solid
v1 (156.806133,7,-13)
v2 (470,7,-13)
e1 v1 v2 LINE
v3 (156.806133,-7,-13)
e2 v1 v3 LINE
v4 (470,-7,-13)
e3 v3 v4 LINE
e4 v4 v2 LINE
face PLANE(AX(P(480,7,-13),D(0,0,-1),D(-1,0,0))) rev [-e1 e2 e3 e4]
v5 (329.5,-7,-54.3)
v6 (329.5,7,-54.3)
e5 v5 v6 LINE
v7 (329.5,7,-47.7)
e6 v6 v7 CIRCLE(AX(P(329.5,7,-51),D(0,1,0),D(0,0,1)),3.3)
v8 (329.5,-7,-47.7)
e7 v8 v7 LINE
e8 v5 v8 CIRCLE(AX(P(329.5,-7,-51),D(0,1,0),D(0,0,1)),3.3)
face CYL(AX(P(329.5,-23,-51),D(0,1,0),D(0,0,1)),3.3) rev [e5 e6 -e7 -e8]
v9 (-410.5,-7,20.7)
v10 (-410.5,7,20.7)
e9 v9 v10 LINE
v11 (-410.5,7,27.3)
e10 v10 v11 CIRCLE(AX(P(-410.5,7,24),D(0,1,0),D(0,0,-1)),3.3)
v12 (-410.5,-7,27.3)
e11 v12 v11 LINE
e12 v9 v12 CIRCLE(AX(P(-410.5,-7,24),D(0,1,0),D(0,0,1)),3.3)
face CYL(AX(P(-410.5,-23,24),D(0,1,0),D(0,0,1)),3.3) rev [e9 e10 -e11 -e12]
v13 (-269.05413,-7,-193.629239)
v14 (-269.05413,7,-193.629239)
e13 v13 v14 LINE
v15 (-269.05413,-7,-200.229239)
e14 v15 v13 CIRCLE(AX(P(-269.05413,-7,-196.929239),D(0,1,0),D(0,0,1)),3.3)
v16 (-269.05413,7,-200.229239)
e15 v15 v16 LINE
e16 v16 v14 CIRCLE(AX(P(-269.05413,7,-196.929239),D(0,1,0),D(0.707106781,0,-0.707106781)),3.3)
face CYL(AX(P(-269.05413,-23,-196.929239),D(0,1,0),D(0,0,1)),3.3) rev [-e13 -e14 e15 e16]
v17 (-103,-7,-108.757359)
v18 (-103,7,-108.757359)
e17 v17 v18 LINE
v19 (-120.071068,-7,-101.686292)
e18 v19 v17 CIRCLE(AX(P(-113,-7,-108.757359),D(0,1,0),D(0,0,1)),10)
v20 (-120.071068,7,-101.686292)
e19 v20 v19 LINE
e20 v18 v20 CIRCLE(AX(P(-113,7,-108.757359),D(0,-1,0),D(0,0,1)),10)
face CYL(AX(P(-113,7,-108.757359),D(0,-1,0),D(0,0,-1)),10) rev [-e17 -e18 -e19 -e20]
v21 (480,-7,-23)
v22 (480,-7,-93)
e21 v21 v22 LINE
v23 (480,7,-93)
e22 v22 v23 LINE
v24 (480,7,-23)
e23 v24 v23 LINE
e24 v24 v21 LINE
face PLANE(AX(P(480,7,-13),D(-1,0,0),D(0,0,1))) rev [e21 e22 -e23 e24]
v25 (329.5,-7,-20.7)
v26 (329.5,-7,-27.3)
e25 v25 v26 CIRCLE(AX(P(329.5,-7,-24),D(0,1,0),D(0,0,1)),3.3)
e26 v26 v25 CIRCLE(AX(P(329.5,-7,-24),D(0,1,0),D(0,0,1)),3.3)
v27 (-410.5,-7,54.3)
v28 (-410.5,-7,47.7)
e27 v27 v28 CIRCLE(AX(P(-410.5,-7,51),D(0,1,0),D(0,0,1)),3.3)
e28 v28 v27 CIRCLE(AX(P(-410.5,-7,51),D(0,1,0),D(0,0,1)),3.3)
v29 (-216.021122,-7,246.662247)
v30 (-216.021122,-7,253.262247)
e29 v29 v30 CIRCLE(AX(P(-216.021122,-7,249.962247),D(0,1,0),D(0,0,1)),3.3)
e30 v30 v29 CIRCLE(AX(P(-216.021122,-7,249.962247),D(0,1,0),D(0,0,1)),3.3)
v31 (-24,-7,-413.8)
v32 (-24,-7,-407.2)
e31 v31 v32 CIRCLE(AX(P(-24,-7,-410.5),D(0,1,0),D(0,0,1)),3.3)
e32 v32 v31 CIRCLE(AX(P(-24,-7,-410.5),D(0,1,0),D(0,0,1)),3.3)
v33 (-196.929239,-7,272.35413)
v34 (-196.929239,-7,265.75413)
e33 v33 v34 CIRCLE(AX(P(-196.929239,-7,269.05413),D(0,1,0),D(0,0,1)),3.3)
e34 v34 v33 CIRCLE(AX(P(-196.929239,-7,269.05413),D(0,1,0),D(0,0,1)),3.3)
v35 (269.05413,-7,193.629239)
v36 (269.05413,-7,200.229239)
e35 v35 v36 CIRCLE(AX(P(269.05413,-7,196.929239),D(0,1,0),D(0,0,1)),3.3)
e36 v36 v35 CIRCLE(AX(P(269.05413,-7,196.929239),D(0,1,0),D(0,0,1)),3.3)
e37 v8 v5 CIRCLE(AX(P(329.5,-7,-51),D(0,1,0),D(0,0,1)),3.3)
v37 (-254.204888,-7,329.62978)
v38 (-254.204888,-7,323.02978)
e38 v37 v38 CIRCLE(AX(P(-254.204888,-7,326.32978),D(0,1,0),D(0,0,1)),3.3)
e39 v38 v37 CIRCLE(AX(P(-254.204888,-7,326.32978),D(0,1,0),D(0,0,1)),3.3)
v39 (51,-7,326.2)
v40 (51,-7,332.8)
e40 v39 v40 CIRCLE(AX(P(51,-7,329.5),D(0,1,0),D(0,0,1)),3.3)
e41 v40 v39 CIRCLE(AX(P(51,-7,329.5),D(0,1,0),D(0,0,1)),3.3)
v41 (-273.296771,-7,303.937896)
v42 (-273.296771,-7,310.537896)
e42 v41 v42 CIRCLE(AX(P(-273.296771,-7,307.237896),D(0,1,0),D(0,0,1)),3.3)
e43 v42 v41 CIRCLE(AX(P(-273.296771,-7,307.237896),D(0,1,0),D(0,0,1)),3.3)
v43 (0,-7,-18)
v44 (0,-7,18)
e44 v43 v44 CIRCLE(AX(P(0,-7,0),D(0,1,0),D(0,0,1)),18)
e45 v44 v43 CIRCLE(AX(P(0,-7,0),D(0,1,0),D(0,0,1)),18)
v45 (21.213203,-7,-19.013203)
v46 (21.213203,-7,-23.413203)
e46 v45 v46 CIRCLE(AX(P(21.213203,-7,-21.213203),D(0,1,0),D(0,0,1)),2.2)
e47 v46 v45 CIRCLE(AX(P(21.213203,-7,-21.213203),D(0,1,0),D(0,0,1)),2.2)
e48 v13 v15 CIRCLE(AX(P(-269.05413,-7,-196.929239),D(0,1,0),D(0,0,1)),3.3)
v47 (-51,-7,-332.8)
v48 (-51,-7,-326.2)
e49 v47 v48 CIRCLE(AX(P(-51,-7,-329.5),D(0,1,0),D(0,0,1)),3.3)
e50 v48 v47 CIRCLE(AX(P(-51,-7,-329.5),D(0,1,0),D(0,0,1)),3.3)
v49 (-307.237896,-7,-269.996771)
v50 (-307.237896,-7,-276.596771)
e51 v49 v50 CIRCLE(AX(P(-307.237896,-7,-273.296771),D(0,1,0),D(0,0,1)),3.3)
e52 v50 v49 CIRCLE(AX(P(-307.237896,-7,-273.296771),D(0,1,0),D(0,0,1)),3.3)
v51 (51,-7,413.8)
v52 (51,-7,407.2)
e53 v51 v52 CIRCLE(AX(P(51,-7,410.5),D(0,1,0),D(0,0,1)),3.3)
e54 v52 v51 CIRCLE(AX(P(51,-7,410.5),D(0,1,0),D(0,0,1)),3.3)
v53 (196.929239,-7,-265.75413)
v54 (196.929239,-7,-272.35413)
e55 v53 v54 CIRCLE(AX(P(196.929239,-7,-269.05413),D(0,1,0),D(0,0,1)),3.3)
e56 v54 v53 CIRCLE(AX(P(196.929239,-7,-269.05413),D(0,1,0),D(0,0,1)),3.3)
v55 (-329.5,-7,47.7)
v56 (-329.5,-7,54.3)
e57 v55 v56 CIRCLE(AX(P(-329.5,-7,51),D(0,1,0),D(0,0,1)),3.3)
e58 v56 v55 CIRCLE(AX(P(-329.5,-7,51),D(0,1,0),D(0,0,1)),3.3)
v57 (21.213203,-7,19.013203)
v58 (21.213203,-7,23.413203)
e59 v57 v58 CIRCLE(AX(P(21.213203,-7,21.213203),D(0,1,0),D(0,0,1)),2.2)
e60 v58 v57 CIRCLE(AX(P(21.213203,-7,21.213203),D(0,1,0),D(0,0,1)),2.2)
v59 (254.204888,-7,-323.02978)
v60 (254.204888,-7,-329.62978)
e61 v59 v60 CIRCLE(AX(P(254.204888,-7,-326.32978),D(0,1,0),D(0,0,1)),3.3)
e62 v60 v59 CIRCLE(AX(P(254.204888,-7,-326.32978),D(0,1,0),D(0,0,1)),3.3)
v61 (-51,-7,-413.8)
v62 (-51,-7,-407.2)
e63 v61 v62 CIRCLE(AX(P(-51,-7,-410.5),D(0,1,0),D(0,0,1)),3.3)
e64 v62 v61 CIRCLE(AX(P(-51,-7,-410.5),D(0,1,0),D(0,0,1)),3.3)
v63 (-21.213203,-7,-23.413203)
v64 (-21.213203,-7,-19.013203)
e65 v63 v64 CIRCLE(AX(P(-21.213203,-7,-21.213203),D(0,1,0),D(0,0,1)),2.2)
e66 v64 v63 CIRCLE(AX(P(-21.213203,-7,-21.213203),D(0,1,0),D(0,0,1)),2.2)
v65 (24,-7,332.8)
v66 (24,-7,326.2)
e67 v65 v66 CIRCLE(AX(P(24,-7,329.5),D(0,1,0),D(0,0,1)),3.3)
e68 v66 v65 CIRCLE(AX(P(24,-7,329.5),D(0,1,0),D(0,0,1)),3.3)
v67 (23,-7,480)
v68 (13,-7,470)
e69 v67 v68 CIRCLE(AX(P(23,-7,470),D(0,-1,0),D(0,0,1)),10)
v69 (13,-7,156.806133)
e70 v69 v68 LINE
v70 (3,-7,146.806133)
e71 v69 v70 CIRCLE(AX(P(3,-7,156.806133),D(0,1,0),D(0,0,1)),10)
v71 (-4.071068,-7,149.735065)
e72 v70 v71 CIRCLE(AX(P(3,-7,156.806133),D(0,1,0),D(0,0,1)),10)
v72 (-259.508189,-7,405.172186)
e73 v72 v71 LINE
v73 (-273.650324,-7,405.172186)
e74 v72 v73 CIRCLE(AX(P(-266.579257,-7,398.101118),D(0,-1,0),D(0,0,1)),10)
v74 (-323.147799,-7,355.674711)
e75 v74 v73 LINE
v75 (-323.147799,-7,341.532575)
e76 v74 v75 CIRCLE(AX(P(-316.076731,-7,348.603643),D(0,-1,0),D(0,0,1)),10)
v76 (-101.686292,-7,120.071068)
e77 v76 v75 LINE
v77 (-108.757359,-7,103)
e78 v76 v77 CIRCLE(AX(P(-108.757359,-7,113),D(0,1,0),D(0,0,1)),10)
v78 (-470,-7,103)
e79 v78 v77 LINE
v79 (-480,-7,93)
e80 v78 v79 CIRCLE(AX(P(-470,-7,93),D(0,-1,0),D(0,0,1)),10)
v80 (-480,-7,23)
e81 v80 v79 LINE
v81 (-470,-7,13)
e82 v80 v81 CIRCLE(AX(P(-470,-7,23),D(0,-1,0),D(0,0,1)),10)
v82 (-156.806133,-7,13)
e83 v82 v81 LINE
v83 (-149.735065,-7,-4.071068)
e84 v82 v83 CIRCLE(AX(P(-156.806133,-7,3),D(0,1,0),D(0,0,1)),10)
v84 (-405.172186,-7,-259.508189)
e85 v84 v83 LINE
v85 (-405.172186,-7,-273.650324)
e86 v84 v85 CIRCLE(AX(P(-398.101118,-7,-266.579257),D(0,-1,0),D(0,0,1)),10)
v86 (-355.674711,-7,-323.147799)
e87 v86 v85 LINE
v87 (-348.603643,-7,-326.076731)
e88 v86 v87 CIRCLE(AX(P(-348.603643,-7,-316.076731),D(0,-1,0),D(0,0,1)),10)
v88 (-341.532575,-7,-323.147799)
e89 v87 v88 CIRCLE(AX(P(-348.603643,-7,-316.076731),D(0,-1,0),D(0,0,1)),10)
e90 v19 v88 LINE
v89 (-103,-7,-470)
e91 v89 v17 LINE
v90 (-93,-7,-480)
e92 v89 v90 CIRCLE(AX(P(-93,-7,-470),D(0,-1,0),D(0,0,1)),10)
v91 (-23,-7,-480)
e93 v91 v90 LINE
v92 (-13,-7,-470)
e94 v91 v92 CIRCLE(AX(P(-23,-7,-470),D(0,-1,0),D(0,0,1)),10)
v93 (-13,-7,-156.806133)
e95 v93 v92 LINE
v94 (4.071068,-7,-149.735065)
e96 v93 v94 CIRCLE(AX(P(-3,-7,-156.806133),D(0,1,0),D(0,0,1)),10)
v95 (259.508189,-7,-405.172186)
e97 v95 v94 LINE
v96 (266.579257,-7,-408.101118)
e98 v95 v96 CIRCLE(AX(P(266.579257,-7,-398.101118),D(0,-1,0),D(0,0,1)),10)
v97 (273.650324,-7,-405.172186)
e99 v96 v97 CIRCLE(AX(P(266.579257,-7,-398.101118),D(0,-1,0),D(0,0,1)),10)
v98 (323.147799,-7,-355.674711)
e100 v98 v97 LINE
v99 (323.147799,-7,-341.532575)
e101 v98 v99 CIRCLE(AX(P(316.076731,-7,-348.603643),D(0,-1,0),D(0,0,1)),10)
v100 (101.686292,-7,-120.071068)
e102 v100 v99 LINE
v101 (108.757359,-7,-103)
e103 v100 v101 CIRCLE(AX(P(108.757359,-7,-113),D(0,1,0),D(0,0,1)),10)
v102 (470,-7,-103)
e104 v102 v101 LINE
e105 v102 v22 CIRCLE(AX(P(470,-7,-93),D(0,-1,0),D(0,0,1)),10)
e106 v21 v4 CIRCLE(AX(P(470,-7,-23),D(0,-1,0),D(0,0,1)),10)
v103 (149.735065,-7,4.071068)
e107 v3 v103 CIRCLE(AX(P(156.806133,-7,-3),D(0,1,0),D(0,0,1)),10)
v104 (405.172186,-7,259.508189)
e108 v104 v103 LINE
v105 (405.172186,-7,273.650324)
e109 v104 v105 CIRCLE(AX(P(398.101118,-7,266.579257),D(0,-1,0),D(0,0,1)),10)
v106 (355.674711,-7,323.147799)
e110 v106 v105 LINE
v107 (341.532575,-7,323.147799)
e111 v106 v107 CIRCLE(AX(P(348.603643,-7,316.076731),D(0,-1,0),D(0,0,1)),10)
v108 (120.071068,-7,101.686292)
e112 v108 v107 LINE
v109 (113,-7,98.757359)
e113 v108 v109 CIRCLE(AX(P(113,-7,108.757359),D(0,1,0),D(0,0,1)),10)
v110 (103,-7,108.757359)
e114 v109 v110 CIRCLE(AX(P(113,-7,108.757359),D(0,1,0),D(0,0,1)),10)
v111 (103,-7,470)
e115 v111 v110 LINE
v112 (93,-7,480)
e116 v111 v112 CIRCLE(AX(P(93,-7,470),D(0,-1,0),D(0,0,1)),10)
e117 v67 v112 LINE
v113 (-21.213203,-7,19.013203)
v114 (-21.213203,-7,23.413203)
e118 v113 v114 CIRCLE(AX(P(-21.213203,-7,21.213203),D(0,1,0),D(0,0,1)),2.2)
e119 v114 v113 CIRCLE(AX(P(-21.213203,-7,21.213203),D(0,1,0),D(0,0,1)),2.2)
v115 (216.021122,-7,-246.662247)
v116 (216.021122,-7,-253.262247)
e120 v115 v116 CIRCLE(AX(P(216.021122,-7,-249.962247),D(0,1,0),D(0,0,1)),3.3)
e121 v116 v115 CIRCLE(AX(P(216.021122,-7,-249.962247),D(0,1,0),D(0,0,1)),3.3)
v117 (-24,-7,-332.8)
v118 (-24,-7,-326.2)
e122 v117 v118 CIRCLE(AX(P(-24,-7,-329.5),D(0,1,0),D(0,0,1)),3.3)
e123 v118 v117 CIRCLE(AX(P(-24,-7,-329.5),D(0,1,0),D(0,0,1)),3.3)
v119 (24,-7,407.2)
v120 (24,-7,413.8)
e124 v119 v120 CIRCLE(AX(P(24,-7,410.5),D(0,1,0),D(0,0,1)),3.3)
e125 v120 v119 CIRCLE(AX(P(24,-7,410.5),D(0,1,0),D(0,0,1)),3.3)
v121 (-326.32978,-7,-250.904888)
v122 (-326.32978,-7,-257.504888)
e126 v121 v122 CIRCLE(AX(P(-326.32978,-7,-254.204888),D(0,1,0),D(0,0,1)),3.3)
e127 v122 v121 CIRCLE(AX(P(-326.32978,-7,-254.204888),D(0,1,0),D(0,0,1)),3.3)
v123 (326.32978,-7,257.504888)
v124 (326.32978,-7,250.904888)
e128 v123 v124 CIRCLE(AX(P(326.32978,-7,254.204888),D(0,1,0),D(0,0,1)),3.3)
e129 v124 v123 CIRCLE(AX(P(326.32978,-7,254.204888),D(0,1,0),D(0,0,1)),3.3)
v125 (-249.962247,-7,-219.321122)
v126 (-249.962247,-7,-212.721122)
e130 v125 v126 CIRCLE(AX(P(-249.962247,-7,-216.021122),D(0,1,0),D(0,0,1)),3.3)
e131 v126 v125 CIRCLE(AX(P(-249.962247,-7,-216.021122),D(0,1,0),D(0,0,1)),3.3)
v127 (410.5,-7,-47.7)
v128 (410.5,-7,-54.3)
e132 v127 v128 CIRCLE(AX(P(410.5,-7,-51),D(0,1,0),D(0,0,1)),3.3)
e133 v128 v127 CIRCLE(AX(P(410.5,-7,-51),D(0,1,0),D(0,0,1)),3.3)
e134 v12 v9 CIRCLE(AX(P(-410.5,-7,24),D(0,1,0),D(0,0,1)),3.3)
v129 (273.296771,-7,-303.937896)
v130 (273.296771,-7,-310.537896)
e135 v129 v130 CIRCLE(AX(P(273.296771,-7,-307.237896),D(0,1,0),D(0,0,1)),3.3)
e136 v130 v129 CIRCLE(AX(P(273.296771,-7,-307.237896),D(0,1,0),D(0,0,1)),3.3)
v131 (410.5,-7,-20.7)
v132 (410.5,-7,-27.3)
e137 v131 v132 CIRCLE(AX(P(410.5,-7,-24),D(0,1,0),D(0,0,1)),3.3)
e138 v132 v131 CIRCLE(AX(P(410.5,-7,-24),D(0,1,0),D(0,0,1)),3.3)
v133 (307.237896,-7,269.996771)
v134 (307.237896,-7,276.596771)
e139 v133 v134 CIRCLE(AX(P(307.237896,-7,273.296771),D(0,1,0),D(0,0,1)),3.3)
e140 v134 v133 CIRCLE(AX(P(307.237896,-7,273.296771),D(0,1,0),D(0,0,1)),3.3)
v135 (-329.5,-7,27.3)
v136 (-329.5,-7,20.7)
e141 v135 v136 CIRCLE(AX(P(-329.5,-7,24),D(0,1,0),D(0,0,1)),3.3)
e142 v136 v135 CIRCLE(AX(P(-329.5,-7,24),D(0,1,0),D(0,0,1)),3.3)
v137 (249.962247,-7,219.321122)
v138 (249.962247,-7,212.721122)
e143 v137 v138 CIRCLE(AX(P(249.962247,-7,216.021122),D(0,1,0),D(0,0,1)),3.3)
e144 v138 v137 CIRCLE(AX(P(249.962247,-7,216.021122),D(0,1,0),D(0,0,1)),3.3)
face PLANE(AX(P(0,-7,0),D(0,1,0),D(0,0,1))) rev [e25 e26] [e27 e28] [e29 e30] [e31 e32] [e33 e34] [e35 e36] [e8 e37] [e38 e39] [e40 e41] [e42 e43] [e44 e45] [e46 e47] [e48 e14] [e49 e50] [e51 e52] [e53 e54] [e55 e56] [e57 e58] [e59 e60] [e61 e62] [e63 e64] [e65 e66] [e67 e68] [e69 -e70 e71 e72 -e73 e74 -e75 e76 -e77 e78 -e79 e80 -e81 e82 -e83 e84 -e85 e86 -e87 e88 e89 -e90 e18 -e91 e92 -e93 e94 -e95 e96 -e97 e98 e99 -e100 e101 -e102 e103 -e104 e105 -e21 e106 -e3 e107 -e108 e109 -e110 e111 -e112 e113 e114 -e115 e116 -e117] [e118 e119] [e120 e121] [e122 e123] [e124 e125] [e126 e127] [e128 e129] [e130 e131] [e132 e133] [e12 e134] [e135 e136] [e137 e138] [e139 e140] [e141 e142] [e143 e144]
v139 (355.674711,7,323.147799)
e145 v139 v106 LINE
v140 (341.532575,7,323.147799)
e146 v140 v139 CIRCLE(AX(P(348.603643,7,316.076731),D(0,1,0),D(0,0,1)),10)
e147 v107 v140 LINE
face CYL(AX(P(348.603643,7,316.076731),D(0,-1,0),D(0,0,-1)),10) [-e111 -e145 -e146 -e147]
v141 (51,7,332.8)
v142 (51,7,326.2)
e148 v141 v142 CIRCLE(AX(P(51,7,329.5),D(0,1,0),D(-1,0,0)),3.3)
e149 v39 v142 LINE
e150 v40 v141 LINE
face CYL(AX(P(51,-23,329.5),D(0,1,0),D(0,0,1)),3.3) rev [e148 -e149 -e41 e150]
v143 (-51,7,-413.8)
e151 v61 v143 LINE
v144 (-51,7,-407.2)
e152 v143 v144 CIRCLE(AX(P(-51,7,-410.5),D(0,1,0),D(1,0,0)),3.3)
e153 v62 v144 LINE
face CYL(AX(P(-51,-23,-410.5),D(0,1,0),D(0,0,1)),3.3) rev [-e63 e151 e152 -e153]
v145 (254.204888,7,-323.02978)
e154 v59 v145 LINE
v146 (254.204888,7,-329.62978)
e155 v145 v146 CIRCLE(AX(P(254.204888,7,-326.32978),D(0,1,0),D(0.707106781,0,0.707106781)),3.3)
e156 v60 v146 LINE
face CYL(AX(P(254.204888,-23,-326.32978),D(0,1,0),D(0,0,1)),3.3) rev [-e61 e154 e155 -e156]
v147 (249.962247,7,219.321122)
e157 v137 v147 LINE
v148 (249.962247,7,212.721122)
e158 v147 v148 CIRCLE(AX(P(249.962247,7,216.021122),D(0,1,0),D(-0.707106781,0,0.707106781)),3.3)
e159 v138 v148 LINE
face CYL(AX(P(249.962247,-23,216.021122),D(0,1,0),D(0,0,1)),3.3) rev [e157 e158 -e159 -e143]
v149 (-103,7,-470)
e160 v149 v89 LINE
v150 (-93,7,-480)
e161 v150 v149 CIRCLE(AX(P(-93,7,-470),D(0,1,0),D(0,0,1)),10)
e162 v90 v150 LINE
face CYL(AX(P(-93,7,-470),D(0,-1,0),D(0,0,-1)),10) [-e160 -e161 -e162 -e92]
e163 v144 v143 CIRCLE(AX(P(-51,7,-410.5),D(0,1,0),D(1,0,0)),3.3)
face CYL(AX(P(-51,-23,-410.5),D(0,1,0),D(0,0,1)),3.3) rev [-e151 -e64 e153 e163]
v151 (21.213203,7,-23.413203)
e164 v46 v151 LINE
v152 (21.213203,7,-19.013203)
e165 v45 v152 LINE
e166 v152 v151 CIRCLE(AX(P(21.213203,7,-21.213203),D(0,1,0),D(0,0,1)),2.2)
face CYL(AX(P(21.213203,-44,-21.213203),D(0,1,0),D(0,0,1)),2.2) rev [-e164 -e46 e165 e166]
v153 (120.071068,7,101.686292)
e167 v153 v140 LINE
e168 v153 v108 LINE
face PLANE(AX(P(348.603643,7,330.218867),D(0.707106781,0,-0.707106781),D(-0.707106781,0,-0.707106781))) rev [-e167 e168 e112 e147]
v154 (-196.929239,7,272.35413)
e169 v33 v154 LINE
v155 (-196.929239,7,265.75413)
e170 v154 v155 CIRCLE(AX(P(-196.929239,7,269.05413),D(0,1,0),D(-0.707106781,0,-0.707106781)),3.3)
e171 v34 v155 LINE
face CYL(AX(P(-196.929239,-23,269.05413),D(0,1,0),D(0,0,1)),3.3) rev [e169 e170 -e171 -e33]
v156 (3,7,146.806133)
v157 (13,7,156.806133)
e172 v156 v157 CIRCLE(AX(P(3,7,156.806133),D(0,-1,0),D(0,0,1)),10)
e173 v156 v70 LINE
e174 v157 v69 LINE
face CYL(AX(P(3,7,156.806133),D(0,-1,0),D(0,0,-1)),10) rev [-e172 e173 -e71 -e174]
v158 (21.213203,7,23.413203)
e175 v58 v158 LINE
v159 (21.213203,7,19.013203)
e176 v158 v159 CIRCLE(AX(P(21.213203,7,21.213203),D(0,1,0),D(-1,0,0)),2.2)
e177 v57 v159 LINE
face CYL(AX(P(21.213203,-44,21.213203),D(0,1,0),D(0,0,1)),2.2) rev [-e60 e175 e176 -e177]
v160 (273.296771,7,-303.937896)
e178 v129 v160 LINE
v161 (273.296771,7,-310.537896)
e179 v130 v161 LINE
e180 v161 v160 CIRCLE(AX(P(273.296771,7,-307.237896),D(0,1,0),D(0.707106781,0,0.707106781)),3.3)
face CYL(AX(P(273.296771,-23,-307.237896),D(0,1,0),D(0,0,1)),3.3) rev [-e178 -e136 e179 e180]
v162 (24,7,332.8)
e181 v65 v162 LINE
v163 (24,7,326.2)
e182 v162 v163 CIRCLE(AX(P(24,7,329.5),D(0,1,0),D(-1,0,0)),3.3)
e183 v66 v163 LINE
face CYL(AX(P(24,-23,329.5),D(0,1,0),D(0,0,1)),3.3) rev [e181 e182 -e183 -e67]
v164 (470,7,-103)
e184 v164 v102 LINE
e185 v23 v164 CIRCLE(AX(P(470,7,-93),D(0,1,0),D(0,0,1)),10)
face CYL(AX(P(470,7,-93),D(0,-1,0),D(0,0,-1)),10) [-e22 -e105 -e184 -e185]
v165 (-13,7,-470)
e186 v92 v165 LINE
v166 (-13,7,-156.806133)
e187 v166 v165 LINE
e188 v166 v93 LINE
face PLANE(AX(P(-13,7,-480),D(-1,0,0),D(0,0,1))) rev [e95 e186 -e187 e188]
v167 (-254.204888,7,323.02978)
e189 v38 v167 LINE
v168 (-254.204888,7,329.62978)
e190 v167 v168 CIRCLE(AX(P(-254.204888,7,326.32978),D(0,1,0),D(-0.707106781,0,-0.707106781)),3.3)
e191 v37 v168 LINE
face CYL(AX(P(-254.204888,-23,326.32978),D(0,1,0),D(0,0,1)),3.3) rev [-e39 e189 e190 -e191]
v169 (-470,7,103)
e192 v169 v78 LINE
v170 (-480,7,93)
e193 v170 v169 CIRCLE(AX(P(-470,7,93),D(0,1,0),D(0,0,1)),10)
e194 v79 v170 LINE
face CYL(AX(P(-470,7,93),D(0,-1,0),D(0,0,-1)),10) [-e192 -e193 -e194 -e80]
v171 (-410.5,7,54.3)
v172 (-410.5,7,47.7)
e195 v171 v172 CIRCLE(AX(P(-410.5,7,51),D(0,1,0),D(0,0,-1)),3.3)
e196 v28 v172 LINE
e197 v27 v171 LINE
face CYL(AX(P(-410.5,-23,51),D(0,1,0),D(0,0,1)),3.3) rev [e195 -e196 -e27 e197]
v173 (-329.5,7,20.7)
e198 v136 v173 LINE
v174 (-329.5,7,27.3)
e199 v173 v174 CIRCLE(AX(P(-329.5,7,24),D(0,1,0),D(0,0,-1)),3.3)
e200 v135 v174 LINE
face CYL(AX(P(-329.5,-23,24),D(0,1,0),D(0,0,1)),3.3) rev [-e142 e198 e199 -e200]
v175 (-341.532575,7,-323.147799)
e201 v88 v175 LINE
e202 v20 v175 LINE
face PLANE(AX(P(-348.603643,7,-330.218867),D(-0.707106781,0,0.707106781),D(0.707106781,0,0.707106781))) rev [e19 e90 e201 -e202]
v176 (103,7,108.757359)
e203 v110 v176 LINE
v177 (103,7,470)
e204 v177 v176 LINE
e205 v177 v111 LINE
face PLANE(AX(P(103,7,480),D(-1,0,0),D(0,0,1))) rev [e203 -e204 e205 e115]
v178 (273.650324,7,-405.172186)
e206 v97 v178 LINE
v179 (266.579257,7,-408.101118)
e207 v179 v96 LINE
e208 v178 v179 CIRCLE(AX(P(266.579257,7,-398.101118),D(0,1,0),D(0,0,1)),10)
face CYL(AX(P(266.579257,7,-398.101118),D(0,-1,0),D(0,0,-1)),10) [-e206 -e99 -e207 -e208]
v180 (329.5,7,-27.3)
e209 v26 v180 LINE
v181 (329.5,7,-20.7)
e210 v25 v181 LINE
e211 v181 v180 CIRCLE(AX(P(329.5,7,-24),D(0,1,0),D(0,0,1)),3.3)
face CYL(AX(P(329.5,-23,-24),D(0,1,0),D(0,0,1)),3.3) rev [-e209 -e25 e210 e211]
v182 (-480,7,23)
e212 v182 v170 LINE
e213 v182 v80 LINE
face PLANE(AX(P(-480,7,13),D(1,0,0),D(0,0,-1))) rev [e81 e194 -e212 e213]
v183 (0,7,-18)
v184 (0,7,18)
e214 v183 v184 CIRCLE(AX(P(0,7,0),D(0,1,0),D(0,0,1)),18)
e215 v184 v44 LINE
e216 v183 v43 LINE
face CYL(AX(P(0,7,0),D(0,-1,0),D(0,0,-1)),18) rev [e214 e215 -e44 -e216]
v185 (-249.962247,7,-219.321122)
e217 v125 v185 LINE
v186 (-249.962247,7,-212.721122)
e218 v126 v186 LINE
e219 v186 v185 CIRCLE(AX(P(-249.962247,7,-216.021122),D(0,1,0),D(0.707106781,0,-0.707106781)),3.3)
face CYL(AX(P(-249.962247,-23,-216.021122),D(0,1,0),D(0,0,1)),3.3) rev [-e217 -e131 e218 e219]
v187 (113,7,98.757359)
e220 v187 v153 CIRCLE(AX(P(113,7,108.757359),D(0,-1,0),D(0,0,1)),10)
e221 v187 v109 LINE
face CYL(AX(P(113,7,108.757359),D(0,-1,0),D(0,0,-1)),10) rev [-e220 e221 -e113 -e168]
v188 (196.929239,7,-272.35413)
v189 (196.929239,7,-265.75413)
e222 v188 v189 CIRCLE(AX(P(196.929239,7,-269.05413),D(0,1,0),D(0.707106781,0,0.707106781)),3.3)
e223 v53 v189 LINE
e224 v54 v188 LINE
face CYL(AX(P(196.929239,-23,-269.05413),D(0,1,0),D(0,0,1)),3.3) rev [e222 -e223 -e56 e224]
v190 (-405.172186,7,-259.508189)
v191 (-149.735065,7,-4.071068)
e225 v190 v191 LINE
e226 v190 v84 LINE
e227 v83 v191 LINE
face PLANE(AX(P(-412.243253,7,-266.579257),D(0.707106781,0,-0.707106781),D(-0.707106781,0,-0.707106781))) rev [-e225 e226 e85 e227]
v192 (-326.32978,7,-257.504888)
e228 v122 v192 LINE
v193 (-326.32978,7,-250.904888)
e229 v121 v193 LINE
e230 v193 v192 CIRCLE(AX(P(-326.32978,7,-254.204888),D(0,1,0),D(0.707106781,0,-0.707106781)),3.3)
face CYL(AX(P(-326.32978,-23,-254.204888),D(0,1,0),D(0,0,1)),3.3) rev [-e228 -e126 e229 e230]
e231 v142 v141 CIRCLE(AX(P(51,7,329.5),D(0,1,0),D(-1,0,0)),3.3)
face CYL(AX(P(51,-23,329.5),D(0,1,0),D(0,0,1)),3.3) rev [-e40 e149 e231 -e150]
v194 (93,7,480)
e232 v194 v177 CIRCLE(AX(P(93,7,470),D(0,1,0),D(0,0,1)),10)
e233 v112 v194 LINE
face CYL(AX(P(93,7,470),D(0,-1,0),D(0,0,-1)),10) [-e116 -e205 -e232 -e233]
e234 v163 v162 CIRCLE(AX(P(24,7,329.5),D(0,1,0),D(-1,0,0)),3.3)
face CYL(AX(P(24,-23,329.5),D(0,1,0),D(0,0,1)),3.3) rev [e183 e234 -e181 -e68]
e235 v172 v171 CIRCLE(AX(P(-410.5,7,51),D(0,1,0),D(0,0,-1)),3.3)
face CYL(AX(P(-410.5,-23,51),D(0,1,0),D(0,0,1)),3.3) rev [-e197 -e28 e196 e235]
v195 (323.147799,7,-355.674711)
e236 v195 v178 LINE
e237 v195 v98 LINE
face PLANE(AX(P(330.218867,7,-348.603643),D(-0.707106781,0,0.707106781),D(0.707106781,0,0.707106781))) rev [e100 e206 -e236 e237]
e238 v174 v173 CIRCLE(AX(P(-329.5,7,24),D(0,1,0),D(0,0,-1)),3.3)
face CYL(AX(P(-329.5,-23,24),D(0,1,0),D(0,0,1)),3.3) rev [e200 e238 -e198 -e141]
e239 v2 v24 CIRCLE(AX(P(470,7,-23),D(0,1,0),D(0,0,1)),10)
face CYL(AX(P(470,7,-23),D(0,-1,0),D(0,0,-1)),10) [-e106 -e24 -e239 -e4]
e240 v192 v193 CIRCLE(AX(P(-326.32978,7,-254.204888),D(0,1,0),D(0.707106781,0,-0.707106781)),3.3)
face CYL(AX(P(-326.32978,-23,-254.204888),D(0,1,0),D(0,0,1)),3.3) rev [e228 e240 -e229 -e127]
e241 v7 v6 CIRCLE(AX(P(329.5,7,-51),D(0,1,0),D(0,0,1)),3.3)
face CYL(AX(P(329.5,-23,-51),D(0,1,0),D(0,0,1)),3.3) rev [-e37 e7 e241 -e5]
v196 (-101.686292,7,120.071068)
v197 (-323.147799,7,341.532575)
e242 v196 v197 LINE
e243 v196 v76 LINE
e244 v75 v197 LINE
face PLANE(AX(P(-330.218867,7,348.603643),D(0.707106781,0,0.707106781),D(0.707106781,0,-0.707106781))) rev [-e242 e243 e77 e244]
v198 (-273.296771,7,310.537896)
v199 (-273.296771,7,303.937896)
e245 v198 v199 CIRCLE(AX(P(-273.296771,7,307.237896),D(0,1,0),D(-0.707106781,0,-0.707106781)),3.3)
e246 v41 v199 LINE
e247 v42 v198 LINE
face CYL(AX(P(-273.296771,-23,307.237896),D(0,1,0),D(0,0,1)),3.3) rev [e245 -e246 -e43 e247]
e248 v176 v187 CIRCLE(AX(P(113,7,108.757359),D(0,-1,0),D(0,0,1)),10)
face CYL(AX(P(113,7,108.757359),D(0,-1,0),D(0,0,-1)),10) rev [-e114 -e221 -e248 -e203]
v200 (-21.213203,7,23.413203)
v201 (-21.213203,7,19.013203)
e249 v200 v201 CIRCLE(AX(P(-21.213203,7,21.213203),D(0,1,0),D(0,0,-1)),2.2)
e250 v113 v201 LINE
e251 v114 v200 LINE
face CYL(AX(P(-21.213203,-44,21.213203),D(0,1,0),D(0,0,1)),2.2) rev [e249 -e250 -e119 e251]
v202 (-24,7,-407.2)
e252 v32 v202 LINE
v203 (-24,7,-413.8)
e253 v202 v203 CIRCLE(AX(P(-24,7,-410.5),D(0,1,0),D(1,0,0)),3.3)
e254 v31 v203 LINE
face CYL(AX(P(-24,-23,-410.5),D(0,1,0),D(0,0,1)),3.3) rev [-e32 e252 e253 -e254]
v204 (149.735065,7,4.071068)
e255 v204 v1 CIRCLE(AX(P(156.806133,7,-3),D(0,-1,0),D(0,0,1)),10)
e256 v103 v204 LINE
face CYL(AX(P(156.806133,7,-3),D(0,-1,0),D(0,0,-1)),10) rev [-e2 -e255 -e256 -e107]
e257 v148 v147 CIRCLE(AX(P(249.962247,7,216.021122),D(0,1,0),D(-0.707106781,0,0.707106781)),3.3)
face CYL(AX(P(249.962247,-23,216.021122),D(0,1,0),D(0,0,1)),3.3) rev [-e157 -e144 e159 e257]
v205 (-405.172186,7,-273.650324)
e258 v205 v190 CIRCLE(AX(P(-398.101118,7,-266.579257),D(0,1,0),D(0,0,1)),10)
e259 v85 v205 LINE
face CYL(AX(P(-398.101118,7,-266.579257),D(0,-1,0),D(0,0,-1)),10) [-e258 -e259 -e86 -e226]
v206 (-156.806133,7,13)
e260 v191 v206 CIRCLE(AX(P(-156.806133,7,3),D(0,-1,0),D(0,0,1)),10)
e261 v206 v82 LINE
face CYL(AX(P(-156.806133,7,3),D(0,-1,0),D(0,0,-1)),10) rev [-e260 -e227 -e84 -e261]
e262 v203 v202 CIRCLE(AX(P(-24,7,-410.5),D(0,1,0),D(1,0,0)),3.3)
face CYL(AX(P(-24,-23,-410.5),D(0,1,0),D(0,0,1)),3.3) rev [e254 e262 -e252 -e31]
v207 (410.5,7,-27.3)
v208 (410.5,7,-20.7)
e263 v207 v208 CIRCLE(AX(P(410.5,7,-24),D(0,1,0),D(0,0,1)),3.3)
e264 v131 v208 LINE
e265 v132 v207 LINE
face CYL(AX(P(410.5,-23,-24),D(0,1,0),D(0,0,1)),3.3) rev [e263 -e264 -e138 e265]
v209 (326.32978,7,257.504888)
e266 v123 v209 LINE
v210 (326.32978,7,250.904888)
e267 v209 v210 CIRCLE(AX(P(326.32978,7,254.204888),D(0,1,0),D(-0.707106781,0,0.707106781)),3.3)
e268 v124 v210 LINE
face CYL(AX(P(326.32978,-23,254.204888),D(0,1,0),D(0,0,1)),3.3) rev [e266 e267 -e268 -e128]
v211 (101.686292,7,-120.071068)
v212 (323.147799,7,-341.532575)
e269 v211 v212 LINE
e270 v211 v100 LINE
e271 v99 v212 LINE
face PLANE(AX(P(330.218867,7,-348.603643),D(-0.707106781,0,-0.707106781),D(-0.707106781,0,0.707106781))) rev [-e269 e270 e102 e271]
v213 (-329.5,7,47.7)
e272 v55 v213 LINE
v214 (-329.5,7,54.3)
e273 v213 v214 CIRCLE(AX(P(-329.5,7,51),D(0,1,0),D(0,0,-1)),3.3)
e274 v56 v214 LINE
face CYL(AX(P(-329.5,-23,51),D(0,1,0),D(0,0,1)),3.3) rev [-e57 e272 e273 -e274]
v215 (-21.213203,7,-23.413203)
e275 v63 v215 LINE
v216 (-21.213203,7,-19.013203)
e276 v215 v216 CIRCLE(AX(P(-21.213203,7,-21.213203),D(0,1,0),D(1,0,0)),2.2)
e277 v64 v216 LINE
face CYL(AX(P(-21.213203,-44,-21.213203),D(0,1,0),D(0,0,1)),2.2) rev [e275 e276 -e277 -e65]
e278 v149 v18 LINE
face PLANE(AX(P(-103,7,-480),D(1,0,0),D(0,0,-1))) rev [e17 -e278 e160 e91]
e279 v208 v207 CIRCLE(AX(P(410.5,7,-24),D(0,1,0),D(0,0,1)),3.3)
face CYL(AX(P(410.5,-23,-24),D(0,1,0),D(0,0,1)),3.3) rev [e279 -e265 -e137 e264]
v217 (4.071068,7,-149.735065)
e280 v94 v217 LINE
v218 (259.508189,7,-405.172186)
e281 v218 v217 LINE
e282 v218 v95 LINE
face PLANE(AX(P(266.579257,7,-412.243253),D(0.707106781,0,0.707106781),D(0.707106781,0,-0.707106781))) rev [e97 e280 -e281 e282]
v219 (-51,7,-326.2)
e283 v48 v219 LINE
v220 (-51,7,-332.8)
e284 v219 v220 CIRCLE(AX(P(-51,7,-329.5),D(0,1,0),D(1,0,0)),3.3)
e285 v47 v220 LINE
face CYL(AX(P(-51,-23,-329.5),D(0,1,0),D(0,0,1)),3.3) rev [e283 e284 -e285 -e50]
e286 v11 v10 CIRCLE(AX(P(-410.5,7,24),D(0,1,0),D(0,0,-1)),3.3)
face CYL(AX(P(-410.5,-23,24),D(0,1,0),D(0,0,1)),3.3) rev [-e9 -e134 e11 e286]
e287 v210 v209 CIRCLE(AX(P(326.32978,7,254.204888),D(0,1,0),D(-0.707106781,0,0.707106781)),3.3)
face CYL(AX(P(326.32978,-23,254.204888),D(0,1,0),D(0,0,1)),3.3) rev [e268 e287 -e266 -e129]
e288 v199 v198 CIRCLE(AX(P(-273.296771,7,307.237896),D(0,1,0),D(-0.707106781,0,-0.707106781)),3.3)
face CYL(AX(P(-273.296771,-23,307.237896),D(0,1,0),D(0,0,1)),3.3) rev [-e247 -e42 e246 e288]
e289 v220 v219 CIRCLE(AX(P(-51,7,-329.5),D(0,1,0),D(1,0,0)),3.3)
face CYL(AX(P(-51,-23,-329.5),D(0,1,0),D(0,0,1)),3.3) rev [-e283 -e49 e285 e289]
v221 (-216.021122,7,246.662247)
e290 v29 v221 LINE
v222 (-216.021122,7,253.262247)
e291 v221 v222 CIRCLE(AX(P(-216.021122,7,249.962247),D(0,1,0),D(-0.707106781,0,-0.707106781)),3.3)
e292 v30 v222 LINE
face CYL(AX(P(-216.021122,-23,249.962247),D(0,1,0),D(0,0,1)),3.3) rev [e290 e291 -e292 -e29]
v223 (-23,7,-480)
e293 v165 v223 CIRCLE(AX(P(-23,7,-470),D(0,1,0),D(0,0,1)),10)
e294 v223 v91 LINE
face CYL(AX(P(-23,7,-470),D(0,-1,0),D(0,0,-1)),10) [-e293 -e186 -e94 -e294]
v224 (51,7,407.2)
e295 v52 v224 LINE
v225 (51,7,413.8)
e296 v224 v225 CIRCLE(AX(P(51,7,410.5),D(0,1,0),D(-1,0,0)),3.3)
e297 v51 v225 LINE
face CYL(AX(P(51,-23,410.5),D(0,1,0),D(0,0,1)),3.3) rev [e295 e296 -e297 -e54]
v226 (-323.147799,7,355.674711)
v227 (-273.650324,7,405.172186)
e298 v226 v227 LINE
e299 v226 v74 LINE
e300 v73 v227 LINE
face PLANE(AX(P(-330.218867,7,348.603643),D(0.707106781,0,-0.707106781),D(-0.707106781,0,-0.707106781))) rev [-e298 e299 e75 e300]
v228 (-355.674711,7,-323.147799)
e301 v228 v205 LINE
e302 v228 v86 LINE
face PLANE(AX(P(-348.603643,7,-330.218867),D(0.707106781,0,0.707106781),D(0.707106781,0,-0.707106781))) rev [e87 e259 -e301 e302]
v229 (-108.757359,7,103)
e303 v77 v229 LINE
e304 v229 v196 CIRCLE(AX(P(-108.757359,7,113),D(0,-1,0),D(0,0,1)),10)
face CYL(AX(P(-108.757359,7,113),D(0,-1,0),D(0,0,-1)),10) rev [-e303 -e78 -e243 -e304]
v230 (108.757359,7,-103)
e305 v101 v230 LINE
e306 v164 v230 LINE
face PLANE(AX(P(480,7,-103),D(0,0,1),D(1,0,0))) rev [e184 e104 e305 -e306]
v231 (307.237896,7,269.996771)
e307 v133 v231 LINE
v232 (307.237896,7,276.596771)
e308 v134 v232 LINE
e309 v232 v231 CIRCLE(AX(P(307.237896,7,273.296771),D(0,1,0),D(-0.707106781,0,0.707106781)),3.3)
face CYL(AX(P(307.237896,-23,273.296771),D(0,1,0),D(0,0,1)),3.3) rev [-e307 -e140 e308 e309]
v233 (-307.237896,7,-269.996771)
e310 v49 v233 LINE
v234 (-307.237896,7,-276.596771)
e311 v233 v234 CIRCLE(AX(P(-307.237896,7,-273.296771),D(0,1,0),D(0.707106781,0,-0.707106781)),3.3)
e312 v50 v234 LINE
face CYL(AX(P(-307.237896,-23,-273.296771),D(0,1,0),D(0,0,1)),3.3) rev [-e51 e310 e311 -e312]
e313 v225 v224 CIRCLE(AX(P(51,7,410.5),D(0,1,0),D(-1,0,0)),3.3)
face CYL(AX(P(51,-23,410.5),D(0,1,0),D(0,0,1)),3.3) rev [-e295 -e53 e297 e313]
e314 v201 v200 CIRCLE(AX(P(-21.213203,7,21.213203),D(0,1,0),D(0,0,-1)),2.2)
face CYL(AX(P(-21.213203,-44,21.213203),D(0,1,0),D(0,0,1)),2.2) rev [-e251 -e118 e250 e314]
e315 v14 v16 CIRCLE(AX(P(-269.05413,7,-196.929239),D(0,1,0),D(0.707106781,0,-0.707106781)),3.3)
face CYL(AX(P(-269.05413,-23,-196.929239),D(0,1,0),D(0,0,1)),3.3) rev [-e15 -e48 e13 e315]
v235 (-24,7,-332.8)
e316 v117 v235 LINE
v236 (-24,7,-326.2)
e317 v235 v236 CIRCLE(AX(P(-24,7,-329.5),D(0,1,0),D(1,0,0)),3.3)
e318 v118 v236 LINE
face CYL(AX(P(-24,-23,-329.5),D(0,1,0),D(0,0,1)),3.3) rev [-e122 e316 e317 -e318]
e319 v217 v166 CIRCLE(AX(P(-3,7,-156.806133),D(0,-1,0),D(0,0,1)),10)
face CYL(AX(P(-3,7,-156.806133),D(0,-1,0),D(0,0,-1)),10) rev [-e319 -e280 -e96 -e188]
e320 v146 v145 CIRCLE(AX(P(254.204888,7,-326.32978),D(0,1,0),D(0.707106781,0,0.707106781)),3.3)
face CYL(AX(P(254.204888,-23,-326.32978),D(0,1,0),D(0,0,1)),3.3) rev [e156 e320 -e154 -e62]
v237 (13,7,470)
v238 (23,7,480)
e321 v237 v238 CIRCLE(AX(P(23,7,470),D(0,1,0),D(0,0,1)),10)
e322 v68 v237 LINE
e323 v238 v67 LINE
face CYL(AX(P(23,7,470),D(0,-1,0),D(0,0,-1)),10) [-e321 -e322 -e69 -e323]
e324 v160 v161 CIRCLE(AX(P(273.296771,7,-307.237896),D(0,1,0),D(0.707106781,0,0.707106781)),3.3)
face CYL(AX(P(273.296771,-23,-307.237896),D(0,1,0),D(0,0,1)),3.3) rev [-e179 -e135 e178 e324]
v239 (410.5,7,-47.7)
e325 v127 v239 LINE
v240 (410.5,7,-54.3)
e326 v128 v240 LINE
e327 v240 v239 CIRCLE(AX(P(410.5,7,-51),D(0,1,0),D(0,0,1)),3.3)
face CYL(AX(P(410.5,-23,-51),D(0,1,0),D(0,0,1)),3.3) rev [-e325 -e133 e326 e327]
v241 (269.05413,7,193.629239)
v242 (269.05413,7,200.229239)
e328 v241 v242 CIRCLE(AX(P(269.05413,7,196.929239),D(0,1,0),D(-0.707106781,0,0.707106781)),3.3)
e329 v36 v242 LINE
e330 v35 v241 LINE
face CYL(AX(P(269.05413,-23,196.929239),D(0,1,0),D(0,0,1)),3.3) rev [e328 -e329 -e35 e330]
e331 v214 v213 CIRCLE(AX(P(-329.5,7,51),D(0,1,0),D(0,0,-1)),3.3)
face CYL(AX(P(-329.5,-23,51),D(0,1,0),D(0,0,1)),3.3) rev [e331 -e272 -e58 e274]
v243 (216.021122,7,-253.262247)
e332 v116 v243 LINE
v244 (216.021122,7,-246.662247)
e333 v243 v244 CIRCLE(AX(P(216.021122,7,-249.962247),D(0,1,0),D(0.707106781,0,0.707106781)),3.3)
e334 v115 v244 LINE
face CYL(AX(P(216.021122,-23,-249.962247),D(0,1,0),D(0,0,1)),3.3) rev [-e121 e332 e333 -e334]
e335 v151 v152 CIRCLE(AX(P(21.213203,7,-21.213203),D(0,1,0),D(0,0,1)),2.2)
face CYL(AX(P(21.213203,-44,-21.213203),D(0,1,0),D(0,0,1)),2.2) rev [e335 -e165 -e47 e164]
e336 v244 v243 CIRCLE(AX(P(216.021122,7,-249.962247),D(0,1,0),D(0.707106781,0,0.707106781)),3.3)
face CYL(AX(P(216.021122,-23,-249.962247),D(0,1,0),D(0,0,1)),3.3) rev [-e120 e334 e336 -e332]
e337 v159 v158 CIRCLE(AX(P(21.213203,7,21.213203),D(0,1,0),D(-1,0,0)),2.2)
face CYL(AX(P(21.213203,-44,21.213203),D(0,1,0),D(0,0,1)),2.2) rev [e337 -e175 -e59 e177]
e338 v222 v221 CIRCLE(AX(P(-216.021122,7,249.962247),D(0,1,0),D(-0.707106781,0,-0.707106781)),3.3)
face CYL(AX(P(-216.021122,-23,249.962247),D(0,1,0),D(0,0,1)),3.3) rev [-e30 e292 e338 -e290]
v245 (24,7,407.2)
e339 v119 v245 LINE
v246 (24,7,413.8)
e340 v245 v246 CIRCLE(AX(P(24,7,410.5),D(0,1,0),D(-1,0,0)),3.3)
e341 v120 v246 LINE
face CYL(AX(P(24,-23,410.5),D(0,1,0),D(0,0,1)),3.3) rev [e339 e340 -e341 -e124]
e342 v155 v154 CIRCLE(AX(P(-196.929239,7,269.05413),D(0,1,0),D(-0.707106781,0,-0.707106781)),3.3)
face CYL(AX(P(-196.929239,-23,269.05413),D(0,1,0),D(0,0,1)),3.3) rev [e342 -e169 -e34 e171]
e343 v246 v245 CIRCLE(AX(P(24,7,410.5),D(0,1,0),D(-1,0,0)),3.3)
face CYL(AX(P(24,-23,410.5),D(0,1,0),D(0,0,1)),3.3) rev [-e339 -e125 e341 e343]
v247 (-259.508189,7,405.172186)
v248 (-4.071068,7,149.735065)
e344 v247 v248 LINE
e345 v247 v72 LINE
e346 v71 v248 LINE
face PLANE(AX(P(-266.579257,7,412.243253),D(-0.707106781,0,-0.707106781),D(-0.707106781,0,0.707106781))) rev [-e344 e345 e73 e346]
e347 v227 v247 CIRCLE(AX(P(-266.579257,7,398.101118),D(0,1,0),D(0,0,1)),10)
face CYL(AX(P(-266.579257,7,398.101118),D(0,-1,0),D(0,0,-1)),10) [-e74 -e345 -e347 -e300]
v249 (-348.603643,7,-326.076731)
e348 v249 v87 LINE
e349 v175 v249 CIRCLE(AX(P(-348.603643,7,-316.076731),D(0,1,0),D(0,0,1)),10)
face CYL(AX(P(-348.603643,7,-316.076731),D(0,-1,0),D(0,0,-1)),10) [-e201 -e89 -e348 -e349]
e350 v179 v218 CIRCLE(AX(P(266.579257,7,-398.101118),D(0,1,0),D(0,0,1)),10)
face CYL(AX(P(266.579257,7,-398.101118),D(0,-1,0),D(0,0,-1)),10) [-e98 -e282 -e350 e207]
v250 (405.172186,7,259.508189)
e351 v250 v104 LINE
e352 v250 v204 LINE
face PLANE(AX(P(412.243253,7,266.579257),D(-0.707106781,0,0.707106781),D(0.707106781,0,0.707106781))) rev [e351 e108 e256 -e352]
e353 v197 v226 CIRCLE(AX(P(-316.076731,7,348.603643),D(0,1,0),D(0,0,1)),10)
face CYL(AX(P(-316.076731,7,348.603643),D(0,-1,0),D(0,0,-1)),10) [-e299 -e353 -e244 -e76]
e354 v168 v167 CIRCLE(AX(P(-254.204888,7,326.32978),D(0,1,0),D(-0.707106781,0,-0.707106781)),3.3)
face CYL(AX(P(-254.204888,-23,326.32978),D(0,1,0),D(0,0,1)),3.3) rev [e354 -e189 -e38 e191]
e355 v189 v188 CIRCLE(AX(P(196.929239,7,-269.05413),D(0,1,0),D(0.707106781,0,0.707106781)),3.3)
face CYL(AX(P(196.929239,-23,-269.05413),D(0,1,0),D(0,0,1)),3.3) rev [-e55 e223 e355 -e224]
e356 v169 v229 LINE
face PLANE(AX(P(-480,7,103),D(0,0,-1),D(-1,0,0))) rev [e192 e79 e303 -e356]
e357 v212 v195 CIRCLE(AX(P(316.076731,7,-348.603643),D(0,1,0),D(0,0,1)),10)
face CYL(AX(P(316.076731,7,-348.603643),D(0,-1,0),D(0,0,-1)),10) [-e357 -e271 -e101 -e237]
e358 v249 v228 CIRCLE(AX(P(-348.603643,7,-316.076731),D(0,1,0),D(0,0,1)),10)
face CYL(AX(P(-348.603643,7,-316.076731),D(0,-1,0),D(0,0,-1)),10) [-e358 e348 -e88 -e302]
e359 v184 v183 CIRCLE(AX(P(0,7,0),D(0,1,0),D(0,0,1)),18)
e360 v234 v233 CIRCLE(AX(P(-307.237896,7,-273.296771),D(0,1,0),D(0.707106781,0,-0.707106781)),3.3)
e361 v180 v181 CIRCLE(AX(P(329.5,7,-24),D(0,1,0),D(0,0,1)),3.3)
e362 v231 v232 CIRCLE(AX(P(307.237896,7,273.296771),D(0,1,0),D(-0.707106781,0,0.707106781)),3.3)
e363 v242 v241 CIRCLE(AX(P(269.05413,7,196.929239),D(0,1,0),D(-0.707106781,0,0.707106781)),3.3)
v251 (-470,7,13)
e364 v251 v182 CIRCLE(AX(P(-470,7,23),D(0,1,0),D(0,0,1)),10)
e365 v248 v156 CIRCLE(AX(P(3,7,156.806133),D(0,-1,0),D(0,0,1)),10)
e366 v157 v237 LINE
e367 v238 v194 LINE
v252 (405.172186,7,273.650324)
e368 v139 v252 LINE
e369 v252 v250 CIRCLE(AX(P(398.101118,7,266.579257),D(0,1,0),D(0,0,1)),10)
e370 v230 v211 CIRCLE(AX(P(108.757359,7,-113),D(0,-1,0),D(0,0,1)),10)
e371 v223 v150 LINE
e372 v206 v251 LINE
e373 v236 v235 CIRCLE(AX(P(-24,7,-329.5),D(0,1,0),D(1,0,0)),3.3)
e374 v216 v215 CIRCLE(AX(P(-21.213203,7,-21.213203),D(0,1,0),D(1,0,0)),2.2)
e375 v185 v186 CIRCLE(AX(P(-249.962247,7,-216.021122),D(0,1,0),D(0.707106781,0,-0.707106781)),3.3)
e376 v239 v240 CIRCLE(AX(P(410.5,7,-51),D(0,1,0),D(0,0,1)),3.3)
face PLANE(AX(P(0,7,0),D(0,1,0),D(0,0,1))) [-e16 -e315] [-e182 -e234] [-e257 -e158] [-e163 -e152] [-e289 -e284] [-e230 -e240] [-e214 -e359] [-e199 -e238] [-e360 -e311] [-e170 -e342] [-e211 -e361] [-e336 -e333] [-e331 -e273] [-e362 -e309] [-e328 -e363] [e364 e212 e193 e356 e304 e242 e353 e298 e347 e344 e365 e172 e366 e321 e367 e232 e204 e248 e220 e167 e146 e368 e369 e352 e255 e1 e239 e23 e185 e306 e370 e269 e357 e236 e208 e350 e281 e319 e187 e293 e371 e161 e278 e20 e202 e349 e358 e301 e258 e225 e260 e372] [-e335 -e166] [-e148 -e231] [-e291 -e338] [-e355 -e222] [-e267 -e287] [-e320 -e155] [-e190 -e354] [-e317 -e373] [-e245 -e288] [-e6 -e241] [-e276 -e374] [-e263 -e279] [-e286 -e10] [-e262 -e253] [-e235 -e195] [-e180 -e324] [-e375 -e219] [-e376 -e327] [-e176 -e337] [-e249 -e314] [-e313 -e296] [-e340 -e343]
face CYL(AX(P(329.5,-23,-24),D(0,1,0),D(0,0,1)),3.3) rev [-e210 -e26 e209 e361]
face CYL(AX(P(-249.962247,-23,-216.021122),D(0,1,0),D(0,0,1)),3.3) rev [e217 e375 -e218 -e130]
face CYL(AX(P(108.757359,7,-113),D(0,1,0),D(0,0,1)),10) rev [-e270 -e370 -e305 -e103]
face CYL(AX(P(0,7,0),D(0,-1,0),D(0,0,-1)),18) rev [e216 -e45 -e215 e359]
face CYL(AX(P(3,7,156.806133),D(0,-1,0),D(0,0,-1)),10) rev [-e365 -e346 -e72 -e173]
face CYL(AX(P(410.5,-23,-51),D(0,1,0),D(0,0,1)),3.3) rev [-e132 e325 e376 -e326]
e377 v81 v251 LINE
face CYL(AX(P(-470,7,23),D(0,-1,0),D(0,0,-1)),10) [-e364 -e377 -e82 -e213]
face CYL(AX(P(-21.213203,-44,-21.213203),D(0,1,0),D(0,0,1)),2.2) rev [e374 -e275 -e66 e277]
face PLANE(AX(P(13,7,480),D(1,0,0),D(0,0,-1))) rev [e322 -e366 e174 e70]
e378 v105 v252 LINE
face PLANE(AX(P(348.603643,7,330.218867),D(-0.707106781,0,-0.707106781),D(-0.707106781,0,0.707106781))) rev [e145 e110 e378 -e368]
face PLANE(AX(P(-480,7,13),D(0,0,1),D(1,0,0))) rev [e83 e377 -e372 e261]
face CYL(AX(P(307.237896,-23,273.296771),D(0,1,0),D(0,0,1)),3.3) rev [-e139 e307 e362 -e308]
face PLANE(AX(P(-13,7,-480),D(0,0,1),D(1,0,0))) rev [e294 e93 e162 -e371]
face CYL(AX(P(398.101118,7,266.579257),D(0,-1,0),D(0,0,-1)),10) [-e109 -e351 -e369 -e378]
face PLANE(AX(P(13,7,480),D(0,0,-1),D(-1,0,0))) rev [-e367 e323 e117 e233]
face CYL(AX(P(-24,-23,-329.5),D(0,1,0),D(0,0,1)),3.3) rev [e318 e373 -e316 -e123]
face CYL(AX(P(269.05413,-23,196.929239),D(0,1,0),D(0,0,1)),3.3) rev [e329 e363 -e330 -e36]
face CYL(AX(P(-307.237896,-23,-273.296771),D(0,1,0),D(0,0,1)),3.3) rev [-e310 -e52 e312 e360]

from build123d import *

# Parameters (mm, degrees)
SKETCH_3_R               = 50
SKETCH_3_R_2             = 18
EXTRUDE_4_DEPTH          = 7
SKETCH_4_W               = 462
SKETCH_4_H               = 90
EXTRUDE_5_DEPTH          = 7
SKETCH_5_R               = 3.3
CUT_EXTRUDE_7_DEPTH      = 30
FILLET_2_R               = 10
PATTERN_CIRCULAR_1_COUNT = 8
FILLET_1_R               = 10
FILLET_3_R               = 10
SKETCH_7_R               = 30
SKETCH_7_R_2             = 18
EXTRUDE_6_DEPTH          = 15
SKETCH_8_R               = 2.75
CUT_EXTRUDE_3_DEPTH      = 50
CUT_EXTRUDE_START        = -29
SKETCH_9_R               = 5
CUT_EXTRUDE_4_DEPTH      = 103
PATTERN_CIRCULAR_2_COUNT = 4
SKETCH_11_R              = 87.380372297
CUT_EXTRUDE_5_DEPTH      = 51
SKETCH_12_R              = 2.2
CUT_EXTRUDE_6_DEPTH      = 51
PATTERN_CIRCULAR_3_COUNT = 4


with BuildPart() as part:
    # 草图3 → 凸台-拉伸4 (new, symmetric)
    with BuildSketch(Plane(origin=(0, 0, 0), x_dir=(1, 0, 0), z_dir=(0, 1, 0))):
        with Locations(Location((0, 0, 0), (0, 0, 270))):
            Circle(SKETCH_3_R)
        with Locations(Location((0, 0, 0), (0, 0, 270))):
            Circle(SKETCH_3_R_2, mode=Mode.SUBTRACT)
    extrude(amount=EXTRUDE_4_DEPTH, both=True)

    # 草图4 → 凸台-拉伸5 (add, symmetric)
    with BuildSketch(Plane(origin=(0, 0, 0), x_dir=(1, 0, 0), z_dir=(0, 1, 0))):
        with Locations((249, 58)):
            Rectangle(SKETCH_4_W, SKETCH_4_H)
    extrude_5 = extrude(amount=EXTRUDE_5_DEPTH, both=True)

    # 草图5 → 切除-拉伸7 (cut)
    with BuildSketch(Plane(origin=(0, 7, 0), x_dir=(1, 0, 0), z_dir=(0, 1, 0))):
        with Locations(Location((329.5, 51, 0), (0, 0, 270))):
            Circle(SKETCH_5_R)
        with Locations(Location((329.5, 24, 0), (0, 0, 270))):
            Circle(SKETCH_5_R)
        with Locations(Location((410.5, 51, 0), (0, 0, 270))):
            Circle(SKETCH_5_R)
        with Locations(Location((410.5, 24, 0), (0, 0, 270))):
            Circle(SKETCH_5_R)
    cut_extrude_7 = extrude(amount=-CUT_EXTRUDE_7_DEPTH, mode=Mode.SUBTRACT)

    # 圆角2
    fillet_2_edges = [part.edges().sort_by_distance(p)[0] for p in [
        (480, 0, -13),
        (480, 0, -103),
    ]]
    fillet(fillet_2_edges, radius=FILLET_2_R)

    # 阵列(圆周)1: 凸台-拉伸5, 切除-拉伸7 ×8 about axis
    pattern_circular_1_axis = Axis((0, 0, 0), (0, 1, 0))
    add([extrude_5.rotate(pattern_circular_1_axis, i * 360 / PATTERN_CIRCULAR_1_COUNT) for i in range(1, PATTERN_CIRCULAR_1_COUNT)])
    add([cut_extrude_7.rotate(pattern_circular_1_axis, i * 360 / PATTERN_CIRCULAR_1_COUNT) for i in range(1, PATTERN_CIRCULAR_1_COUNT)], mode=Mode.SUBTRACT)

    # 圆角1
    fillet_1_edges = [part.edges().sort_by_distance(p)[0] for p in [
        (-13, 0, -132.663996924),
        (84.615223689, 0, -103),
        (132.663996924, 0, -13),
        (103, 0, 84.615223689),
        (13, 0, 132.663996924),
        (-84.615223689, 0, 103),
        (-132.663996924, 0, 13),
        (-103, 0, -84.615223689),
    ]]
    fillet(fillet_1_edges, radius=FILLET_1_R)

    # 圆角3
    fillet_3_edges = [part.edges().sort_by_distance(p)[0] for p in [
        (-13, 0, -480),
        (266.579256507, 0, -412.243253432),
        (330.218866814, 0, -348.603643125),
        (412.243253432, 0, 266.579256507),
        (348.603643125, 0, 330.218866814),
        (103, 0, 480),
        (13, 0, 480),
        (-266.579256507, 0, 412.243253432),
        (-330.218866814, 0, 348.603643125),
        (-480, 0, 103),
        (-480, 0, 13),
        (-412.243253432, 0, -266.579256507),
        (-348.603643125, 0, -330.218866814),
        (-103, 0, -480),
    ]]
    fillet(fillet_3_edges, radius=FILLET_3_R)

    # 草图7 → 凸台-拉伸6 (add)
    with BuildSketch(Plane(origin=(0, 7, 0), x_dir=(1, 0, 0), z_dir=(0, 1, 0))):
        with Locations(Location((0, 0, 0), (0, 0, 270))):
            Circle(SKETCH_7_R)
        with Locations(Location((0, 0, 0), (0, 0, 270))):
            Circle(SKETCH_7_R_2, mode=Mode.SUBTRACT)
    extrude(amount=EXTRUDE_6_DEPTH)

    # 草图8 → 切除-拉伸3 (cut)
    with BuildSketch(Plane(origin=(0, 0, 0), x_dir=(0, 0, -1), z_dir=(1, 0, 0))):
        with Locations((0, 15)):
            Circle(SKETCH_8_R)
    cut_extrude_3 = extrude(amount=-CUT_EXTRUDE_3_DEPTH, mode=Mode.SUBTRACT)

    # 草图9 → 切除-拉伸4 (cut)
    with BuildSketch(Plane(origin=(0, 0, 0), x_dir=(0, 0, -1), z_dir=(1, 0, 0)).offset(CUT_EXTRUDE_START)):
        with Locations((0, 15)):
            Circle(SKETCH_9_R)
    cut_extrude_4 = extrude(amount=-CUT_EXTRUDE_4_DEPTH, mode=Mode.SUBTRACT)

    # 阵列(圆周)2: 切除-拉伸3, 切除-拉伸4 ×4 about axis
    pattern_circular_2_axis = Axis((0, 0, 0), (0, 1, 0))
    add([cut_extrude_3.rotate(pattern_circular_2_axis, i * 360 / PATTERN_CIRCULAR_2_COUNT) for i in range(1, PATTERN_CIRCULAR_2_COUNT)], mode=Mode.SUBTRACT)
    add([cut_extrude_4.rotate(pattern_circular_2_axis, i * 360 / PATTERN_CIRCULAR_2_COUNT) for i in range(1, PATTERN_CIRCULAR_2_COUNT)], mode=Mode.SUBTRACT)

    # 草图11 → 切除-拉伸5 (cut)
    with BuildSketch(Plane(origin=(0, 7, 0), x_dir=(1, 0, 0), z_dir=(0, 1, 0))):
        Circle(SKETCH_11_R)
    extrude(amount=CUT_EXTRUDE_5_DEPTH, mode=Mode.SUBTRACT)

    # 草图12 → 切除-拉伸6 (cut)
    with BuildSketch(Plane(origin=(0, 7, 0), x_dir=(1, 0, 0), z_dir=(0, 1, 0))):
        with Locations(Location((21.213203436, 21.213203436, 0), (0, 0, 270))):
            Circle(SKETCH_12_R)
    cut_extrude_6 = extrude(amount=-CUT_EXTRUDE_6_DEPTH, mode=Mode.SUBTRACT)

    # 阵列(圆周)3: 切除-拉伸6 ×4 about axis
    pattern_circular_3_axis = Axis((0, 0, 0), (0, 1, 0))
    for i in range(1, PATTERN_CIRCULAR_3_COUNT):
        add(cut_extrude_6.rotate(pattern_circular_3_axis, i * 360 / PATTERN_CIRCULAR_3_COUNT), mode=Mode.SUBTRACT)


solid = part.part
